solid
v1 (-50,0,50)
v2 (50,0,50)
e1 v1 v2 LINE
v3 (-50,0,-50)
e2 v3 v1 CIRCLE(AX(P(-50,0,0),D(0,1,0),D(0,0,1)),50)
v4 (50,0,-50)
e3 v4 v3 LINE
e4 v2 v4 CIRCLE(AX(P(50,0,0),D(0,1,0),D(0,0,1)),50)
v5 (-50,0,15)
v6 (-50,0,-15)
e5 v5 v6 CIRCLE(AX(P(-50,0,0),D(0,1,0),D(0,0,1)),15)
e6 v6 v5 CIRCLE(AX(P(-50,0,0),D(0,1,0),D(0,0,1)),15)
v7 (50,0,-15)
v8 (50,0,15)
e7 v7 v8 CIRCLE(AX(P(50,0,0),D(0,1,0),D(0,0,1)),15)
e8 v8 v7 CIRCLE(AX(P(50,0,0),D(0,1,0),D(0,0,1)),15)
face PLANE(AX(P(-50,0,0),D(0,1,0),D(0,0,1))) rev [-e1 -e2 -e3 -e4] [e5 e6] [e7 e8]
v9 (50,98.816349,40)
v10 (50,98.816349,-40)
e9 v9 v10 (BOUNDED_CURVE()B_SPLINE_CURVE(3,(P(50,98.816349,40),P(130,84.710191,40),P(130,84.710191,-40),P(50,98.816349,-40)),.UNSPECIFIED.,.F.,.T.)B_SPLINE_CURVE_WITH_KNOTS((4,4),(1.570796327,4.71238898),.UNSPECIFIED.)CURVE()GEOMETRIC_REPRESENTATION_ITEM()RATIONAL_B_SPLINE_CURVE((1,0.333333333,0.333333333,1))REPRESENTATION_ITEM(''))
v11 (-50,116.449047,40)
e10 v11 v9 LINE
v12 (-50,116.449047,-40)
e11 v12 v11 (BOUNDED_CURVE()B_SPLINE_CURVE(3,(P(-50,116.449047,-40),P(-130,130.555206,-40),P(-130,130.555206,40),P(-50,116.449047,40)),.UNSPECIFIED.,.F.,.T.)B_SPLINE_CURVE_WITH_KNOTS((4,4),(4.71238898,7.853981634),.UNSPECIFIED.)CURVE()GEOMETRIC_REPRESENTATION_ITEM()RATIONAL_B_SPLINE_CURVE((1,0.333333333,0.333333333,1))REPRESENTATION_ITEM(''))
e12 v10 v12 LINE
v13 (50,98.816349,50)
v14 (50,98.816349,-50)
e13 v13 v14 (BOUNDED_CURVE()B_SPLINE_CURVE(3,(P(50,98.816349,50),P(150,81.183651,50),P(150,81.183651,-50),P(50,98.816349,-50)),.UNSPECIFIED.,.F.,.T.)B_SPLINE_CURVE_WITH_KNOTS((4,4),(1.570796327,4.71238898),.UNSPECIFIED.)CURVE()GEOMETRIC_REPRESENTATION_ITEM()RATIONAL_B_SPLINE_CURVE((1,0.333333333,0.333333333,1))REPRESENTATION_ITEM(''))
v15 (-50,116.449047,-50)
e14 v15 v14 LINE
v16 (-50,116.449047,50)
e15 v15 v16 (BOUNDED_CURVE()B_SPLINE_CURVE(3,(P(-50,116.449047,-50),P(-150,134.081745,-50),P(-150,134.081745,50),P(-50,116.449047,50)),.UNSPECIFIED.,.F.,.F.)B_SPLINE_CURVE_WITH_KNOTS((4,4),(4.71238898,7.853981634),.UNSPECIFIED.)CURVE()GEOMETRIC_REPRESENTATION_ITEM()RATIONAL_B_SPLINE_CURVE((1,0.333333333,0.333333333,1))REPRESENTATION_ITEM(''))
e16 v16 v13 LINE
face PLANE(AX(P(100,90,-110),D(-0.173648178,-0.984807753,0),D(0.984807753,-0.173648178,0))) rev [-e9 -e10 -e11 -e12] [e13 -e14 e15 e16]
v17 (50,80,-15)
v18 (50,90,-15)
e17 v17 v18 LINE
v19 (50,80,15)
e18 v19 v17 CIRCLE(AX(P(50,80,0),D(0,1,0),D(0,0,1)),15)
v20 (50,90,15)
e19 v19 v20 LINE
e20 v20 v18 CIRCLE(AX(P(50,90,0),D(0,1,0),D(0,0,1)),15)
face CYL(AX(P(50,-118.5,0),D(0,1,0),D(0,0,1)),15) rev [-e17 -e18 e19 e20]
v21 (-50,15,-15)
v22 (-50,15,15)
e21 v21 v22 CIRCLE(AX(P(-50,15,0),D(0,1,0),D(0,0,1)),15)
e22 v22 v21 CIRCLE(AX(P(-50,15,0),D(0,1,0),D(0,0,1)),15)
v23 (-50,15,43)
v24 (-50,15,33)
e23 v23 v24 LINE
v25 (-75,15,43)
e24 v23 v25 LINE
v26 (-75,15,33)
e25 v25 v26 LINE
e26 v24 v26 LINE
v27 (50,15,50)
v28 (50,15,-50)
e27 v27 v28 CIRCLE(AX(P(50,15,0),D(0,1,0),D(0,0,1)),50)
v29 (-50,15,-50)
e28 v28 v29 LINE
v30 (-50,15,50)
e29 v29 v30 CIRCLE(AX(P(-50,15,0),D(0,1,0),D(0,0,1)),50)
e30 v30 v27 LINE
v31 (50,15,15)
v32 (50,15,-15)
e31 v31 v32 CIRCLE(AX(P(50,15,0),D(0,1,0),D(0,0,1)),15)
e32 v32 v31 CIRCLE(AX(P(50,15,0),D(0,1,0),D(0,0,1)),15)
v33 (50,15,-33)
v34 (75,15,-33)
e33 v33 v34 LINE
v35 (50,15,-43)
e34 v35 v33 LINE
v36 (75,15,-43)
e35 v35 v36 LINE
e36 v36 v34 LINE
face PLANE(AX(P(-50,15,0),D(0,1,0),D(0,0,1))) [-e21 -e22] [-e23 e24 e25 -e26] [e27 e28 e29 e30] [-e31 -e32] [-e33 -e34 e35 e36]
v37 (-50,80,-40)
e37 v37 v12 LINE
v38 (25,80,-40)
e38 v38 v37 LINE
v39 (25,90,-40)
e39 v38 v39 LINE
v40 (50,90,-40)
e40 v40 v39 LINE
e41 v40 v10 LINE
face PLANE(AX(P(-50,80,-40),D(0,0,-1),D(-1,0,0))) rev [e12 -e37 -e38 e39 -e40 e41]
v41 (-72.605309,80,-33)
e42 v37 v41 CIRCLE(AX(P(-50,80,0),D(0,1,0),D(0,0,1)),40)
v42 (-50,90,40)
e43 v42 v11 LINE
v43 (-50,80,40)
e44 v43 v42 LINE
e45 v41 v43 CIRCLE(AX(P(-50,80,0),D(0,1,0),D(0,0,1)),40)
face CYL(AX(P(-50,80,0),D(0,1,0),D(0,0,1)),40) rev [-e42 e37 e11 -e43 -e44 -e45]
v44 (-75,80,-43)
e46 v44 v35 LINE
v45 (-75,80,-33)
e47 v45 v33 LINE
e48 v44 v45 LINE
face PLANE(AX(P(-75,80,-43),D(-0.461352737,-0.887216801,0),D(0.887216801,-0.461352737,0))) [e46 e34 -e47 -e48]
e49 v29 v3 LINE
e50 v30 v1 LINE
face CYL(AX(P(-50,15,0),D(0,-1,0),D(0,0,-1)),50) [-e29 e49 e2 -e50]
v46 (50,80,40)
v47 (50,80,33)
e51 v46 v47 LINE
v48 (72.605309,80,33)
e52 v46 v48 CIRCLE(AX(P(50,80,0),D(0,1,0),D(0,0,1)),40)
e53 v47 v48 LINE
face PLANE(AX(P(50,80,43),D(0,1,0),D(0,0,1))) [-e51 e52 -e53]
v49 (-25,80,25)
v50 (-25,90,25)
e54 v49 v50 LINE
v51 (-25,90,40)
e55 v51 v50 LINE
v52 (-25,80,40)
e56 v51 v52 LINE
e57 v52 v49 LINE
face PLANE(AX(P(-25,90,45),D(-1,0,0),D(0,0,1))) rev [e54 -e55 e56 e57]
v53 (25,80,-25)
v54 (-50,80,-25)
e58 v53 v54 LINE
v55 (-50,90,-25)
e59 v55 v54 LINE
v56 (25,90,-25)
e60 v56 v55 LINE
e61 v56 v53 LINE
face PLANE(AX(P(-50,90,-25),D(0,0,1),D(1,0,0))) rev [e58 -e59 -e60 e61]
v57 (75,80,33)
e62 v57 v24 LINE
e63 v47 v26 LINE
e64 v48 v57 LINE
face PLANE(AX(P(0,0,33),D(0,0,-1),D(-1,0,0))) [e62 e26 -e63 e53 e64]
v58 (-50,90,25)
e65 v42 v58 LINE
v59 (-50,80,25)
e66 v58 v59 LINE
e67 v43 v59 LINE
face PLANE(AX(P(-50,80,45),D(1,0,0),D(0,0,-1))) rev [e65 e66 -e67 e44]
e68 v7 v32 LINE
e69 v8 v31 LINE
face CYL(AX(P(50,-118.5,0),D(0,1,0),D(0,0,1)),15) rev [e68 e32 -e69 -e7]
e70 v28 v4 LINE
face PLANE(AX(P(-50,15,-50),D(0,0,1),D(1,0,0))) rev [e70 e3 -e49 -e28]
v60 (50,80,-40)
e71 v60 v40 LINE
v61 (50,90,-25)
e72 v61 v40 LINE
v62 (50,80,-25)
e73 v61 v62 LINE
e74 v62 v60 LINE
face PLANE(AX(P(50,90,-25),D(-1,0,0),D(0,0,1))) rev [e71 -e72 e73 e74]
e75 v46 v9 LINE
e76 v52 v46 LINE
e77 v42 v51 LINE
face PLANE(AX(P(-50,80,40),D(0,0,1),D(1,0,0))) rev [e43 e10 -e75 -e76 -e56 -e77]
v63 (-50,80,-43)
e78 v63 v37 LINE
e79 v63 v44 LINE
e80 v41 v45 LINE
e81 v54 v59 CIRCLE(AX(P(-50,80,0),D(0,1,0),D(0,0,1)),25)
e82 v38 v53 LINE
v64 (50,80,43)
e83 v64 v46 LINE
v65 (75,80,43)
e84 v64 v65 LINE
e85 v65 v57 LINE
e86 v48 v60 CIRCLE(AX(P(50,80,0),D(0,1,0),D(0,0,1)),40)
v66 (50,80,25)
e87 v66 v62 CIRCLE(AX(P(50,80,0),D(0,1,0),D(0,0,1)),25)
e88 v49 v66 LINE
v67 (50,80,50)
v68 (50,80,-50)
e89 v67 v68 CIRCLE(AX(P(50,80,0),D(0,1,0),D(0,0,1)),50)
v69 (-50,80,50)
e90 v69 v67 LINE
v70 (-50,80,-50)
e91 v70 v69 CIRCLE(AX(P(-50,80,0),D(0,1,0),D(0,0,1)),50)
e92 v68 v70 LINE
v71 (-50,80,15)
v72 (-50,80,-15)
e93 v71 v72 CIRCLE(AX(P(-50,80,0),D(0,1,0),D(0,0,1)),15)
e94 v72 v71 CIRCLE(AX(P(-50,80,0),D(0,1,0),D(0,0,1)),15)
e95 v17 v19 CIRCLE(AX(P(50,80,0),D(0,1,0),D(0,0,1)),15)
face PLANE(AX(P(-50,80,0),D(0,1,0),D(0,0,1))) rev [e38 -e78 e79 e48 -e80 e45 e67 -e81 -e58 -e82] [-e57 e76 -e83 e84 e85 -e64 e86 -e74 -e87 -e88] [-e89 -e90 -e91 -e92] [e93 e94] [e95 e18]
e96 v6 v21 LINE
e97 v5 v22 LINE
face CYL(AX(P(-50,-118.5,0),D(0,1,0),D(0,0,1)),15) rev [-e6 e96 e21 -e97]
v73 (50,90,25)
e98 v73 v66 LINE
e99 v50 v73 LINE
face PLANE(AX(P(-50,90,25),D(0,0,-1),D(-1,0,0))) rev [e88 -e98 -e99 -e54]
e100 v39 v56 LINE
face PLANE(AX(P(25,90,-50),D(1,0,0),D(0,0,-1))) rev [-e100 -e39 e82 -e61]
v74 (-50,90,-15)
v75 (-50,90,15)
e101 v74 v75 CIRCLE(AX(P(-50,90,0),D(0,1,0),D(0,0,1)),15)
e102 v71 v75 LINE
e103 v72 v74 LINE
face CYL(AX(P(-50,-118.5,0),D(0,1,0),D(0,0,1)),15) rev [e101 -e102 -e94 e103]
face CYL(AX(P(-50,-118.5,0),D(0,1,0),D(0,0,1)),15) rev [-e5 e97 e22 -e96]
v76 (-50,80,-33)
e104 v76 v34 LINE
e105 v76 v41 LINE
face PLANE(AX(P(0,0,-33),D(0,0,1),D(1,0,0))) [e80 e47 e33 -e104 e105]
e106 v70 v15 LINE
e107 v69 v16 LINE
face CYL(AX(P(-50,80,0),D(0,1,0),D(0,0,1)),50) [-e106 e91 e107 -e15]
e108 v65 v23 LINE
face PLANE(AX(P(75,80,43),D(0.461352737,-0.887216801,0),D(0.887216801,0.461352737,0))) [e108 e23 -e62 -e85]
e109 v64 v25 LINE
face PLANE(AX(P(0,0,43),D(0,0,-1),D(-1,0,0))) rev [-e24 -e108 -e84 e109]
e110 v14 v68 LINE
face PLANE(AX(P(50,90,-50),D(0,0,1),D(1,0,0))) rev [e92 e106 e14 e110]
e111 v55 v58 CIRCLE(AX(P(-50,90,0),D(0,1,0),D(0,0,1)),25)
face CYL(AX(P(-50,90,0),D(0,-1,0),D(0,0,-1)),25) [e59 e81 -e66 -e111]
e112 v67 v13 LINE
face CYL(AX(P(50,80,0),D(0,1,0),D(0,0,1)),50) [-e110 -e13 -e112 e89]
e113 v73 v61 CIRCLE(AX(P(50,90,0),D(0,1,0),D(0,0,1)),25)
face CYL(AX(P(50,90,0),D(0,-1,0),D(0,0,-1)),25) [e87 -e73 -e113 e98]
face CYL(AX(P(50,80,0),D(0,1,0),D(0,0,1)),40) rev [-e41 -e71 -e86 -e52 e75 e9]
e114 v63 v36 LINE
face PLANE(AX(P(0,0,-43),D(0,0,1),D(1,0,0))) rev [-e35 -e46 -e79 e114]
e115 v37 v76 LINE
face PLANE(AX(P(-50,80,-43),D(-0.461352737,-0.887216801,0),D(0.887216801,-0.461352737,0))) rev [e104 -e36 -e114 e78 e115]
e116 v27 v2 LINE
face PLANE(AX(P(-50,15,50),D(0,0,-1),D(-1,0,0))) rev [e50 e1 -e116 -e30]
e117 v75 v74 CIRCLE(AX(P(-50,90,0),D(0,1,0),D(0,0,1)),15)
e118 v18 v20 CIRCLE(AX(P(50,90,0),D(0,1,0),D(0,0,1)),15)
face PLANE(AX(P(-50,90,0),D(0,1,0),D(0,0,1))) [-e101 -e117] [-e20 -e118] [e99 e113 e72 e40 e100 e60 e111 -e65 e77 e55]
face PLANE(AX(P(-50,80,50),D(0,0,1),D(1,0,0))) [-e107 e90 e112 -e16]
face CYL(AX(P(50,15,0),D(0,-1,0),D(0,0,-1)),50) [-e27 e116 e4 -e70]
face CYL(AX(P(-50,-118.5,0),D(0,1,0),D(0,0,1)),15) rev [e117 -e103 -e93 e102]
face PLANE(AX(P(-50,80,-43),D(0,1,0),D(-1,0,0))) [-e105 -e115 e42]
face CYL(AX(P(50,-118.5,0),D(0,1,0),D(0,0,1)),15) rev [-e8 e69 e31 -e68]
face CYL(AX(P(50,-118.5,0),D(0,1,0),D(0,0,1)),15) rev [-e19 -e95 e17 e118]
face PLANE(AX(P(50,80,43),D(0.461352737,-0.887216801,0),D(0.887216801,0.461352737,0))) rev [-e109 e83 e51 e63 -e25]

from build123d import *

# Parameters (mm, degrees)
BASE_PLATE_DEPTH         = 15
UPPER_PLATE_DEPTH        = 10
LOOP_WALL_DEPTH          = 50
LOOP_WALL_DEPTH_BACK     = 10
WALL_OPENING_CUT_DEPTH   = 160
TAB_SKETCH_W             = 25
TAB_SKETCH_H             = 10
TAB_DEPTH                = 20
GUIDE_RAIL_1_DEPTH       = 7
GUIDE_RAIL_1_DEPTH_BACK  = 3
GUIDE_RAIL_2_DEPTH       = 7
GUIDE_RAIL_2_DEPTH_BACK  = 3
ANGLED_TRIM_CUT_SKETCH_R = 15
ANGLED_TRIM_CUT_DEPTH    = 133.5


with BuildPart() as part:
    # Base Plate Sketch → Base Plate (new body)
    with BuildSketch(Plane(origin=(0, 0, 0), x_dir=(1, 0, 0), z_dir=(0, 1, 0))):
        with BuildLine():
            Line((-50, 50), (50, 50))
            ThreePointArc((50, 50), (100, 0), (50, -50))
            Line((50, -50), (-50, -50))
            ThreePointArc((-50, -50), (-100, 0), (-50, 50))
        make_face()
    extrude(amount=BASE_PLATE_DEPTH)



with BuildPart() as body_2:
    # Upper Plate Sketch → Upper Plate (new body)
    with BuildSketch(Plane(origin=(0, 80, 0), x_dir=(1, 0, 0), z_dir=(0, 1, 0))):
        with BuildLine():
            Line((50, 50), (25, 50))
            Line((25, 50), (25, 25))
            Line((25, 25), (-50, 25))
            ThreePointArc((-50, 25), (-75, 0), (-50, -25))
            Line((-50, -25), (50, -25))
            ThreePointArc((50, -25), (75, 0), (50, 25))
            Line((50, 25), (50, 50))
        make_face()
    extrude(amount=UPPER_PLATE_DEPTH)

    # Loop Wall Sketch → Loop Wall (add, two sides: drawn at the far end of the back side and taken through both)
    with BuildSketch(Plane(origin=(0, 90, 0), x_dir=(1, 0, 0), z_dir=(0, 1, 0)).offset(-LOOP_WALL_DEPTH_BACK)):
        with BuildLine():
            Line((-50, 50), (50, 50))
            ThreePointArc((50, 50), (100, 0), (50, -50))
            Line((50, -50), (-50, -50))
            ThreePointArc((-50, -50), (-100, 0), (-50, 50))
        make_face()
        with BuildLine():
            Line((-50, 40), (50, 40))
            ThreePointArc((50, 40), (90, 0), (50, -40))
            Line((50, -40), (-50, -40))
            ThreePointArc((-50, -40), (-90, 0), (-50, 40))
        make_face(mode=Mode.SUBTRACT)
    extrude(amount=LOOP_WALL_DEPTH + LOOP_WALL_DEPTH_BACK)

    # Wall Opening Cut Sketch → Wall Opening Cut (cut, symmetric)
    with BuildSketch(Plane.XY.offset(50)):
        Polygon((100, 90), (-100, 125.265396142), (-100, 140), (100, 140), align=None)
    extrude(amount=WALL_OPENING_CUT_DEPTH, both=True, mode=Mode.SUBTRACT)

    # Tab Sketch → Tab (add)
    with BuildSketch(Plane.XY.offset(25)):
        with Locations((-37.5, 85)):
            Rectangle(TAB_SKETCH_W, TAB_SKETCH_H)
    extrude(amount=TAB_DEPTH)


with BuildPart() as part_1:
    add(part.part)

    add(body_2.part)  # Guide Rail 1 merges body 2
    # Guide Rail 1 Sketch → Guide Rail 1 (add, two sides: drawn at the far end of the back side and taken through both)
    with BuildSketch(Plane.XY.offset(-40).offset(-GUIDE_RAIL_1_DEPTH_BACK)):
        Polygon((50, 15), (75, 15), (-50, 80), (-75, 80), align=None)
    extrude(amount=GUIDE_RAIL_1_DEPTH + GUIDE_RAIL_1_DEPTH_BACK)

    # Guide Rail 2 Sketch → Guide Rail 2 (add, two sides: drawn at the far end of the back side and taken through both)
    with BuildSketch(Plane(origin=(0, 0, 40), x_dir=(-1, 0, 0), z_dir=(0, 0, -1)).offset(-GUIDE_RAIL_2_DEPTH_BACK)):
        Polygon((50, 15), (75, 15), (-50, 80), (-75, 80), align=None)
    extrude(amount=GUIDE_RAIL_2_DEPTH + GUIDE_RAIL_2_DEPTH_BACK)

    # Angled Trim Cut Sketch → Angled Trim Cut (cut, symmetric)
    with BuildSketch(Plane(origin=(0, 15, 0), x_dir=(1, 0, 0), z_dir=(0, 1, 0))):
        with Locations(Location((-50, 0, 0), (0, 0, 270))):
            Circle(ANGLED_TRIM_CUT_SKETCH_R)
        with Locations(Location((50, 0, 0), (0, 0, 270))):
            Circle(ANGLED_TRIM_CUT_SKETCH_R)
    extrude(amount=ANGLED_TRIM_CUT_DEPTH, both=True, mode=Mode.SUBTRACT)


solid = part_1.part
